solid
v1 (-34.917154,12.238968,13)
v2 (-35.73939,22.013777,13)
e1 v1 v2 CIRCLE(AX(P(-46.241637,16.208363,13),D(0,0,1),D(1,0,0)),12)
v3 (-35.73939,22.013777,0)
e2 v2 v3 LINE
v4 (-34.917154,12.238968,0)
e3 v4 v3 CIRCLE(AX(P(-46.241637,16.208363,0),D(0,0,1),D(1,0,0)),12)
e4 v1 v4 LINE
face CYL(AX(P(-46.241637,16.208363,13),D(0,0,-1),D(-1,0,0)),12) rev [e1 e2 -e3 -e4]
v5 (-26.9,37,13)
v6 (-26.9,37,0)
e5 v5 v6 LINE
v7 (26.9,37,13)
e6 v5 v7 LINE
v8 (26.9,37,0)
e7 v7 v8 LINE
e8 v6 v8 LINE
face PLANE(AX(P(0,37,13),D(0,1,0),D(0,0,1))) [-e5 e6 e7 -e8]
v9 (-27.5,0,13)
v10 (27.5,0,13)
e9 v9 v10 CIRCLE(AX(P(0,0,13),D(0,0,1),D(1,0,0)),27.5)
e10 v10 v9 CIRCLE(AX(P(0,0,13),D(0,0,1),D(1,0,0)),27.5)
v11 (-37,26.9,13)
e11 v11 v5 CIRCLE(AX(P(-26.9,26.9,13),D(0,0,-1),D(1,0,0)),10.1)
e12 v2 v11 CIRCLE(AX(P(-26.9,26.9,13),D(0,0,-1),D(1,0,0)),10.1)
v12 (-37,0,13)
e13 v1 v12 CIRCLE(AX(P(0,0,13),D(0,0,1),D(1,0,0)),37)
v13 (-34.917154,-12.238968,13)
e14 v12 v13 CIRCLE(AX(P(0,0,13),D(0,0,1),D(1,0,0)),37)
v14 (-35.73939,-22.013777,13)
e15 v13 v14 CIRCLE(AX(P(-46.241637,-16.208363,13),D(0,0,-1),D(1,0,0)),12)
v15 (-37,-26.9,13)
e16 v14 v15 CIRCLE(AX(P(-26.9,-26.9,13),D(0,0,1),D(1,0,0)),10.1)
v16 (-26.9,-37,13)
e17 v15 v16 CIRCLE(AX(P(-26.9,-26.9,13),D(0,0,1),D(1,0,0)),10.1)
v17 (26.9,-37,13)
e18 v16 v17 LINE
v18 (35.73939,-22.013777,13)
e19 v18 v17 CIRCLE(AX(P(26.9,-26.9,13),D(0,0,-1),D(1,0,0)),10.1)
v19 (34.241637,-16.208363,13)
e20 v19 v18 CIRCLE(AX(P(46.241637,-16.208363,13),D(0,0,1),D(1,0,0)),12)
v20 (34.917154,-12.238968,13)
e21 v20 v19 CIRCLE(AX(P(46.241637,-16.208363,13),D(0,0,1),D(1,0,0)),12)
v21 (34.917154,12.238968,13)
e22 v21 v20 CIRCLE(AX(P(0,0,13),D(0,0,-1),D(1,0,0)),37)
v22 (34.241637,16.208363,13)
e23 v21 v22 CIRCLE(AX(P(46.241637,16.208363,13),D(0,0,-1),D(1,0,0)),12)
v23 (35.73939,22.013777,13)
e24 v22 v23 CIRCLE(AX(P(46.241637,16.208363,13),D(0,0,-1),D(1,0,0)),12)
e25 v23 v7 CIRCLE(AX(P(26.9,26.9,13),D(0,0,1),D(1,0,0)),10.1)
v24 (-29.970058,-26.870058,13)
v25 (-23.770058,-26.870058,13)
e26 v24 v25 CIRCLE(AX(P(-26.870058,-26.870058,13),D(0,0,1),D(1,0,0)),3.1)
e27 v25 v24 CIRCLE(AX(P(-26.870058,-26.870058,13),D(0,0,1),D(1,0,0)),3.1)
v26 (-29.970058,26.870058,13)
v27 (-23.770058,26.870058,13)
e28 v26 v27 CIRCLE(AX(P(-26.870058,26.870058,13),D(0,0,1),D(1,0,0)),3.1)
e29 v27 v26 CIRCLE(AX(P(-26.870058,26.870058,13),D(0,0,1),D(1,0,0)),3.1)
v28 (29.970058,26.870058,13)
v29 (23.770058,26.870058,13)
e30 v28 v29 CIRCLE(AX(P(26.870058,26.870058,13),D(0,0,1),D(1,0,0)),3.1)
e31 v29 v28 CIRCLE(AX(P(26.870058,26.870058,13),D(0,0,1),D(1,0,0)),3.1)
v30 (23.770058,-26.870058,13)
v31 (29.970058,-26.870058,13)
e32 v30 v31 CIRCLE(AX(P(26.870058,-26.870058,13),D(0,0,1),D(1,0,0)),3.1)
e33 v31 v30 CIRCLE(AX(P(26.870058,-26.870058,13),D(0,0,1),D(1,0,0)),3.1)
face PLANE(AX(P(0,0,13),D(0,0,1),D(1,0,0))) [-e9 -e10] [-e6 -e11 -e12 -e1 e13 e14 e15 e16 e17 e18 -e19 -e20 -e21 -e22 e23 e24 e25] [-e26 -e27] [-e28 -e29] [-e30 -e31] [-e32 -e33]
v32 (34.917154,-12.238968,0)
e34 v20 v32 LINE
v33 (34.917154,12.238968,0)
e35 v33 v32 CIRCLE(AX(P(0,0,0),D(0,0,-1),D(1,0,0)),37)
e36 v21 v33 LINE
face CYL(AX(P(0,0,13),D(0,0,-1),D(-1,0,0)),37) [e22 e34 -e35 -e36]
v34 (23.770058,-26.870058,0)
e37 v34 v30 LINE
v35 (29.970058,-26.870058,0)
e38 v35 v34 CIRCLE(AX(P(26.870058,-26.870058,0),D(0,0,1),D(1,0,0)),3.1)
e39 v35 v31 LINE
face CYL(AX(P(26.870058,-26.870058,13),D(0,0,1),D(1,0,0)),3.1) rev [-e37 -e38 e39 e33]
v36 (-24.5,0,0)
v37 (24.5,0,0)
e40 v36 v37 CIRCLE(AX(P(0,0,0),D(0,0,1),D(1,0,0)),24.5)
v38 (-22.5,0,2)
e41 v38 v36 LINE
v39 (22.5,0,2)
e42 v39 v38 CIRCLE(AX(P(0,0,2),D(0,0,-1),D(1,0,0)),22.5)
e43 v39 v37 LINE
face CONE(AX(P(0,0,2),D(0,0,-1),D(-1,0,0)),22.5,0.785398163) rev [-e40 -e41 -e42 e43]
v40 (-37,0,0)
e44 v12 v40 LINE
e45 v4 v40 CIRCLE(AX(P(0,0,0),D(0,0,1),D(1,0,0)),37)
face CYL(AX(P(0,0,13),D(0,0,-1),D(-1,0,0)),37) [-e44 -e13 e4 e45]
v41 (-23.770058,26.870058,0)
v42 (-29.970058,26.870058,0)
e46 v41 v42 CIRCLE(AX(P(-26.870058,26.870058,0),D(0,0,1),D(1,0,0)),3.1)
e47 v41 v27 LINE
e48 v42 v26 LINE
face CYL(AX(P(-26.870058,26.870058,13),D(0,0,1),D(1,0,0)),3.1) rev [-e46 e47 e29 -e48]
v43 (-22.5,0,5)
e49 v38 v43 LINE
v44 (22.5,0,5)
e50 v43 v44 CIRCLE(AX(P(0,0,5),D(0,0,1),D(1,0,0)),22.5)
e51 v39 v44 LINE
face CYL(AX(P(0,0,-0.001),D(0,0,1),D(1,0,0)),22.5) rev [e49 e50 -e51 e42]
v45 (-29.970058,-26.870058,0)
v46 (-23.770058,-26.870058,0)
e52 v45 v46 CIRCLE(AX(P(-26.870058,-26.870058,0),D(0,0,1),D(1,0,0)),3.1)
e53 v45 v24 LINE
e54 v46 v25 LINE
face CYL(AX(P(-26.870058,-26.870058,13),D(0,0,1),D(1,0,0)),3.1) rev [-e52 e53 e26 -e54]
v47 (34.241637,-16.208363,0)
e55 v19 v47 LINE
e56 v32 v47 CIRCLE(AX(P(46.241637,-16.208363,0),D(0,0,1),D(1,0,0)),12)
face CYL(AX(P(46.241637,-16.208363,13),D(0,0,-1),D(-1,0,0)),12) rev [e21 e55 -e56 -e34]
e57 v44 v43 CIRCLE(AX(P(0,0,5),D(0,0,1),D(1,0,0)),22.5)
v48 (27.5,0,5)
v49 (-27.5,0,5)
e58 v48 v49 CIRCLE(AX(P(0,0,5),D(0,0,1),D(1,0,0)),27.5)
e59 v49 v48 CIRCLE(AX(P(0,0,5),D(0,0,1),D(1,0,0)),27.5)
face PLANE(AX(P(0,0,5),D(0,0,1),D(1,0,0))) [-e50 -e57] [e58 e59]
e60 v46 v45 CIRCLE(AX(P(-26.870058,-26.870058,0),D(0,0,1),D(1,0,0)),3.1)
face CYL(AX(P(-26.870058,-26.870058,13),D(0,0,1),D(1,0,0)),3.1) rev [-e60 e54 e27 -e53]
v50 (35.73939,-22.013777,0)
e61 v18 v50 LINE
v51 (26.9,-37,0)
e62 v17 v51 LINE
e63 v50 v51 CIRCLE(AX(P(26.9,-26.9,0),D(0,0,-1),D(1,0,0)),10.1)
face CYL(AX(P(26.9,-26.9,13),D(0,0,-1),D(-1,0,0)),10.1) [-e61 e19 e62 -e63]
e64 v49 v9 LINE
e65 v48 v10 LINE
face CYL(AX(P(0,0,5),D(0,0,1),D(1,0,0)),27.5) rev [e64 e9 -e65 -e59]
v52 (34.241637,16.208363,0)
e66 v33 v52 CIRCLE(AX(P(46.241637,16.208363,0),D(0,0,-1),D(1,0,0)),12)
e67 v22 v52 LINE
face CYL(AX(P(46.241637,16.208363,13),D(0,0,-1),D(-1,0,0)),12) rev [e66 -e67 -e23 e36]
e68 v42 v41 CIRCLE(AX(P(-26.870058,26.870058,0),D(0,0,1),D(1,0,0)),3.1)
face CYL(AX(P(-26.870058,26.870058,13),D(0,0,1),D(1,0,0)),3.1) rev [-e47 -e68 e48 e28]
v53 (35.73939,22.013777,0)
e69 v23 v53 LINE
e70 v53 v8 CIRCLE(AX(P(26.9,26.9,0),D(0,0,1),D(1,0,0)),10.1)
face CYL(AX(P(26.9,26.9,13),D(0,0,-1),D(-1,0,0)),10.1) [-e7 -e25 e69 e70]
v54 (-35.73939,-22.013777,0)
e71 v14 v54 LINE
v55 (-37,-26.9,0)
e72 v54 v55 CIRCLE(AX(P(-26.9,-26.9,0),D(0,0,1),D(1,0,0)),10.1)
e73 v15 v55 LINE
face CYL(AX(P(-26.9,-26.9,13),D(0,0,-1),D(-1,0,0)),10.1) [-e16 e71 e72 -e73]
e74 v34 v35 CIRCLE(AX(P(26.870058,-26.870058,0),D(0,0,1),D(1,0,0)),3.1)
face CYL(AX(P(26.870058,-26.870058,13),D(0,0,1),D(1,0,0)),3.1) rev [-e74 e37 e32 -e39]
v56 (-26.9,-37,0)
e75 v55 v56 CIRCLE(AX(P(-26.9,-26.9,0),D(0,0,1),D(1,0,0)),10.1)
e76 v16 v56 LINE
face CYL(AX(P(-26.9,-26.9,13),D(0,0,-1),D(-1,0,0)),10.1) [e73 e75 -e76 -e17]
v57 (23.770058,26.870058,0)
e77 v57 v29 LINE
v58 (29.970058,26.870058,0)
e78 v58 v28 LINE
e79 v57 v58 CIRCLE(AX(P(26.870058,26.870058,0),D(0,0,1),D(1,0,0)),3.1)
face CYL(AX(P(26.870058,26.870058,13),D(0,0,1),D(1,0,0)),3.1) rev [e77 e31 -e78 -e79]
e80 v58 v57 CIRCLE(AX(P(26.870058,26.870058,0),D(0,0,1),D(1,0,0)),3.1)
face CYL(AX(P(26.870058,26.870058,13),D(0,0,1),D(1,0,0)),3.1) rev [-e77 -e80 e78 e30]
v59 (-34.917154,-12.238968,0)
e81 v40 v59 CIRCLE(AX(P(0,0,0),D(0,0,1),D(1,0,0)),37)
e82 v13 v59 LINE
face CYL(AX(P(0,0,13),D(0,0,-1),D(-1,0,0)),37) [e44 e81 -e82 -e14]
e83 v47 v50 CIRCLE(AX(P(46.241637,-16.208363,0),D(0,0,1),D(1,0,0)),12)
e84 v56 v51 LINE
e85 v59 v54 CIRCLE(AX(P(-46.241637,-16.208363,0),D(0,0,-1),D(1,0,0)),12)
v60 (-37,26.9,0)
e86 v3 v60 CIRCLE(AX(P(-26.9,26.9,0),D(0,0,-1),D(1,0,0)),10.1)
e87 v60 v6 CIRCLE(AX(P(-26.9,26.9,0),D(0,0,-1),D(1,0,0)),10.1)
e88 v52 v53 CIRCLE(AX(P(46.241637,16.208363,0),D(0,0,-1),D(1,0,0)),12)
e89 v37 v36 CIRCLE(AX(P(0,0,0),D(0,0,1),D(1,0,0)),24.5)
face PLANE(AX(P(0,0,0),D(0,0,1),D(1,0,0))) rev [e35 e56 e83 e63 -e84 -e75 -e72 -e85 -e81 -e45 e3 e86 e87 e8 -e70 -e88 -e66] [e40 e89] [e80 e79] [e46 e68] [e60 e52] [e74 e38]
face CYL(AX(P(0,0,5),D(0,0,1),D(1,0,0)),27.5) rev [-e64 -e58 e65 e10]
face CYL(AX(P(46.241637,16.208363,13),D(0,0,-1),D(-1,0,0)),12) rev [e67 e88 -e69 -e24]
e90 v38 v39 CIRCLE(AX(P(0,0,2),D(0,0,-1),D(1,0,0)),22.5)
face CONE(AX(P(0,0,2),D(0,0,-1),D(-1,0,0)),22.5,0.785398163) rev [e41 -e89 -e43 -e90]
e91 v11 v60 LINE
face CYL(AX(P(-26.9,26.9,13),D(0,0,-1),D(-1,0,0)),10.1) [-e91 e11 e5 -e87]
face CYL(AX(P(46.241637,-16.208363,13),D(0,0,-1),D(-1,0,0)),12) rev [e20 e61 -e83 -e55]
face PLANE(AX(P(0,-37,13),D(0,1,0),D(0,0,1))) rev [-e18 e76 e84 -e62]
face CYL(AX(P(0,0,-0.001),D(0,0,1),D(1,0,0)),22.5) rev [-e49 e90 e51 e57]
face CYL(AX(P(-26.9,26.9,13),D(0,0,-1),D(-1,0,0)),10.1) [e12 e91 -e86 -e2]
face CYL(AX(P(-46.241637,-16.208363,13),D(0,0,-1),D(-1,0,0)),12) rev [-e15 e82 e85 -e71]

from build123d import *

# Parameters (mm, degrees)
EXTRUDE_1_DEPTH         = 13
HOLE_WIZARD_6_2_6_2_1_D = 6.2
SKETCH_4_R              = 27.5
CUT_EXTRUDE_1_DEPTH     = 8
CUT_EXTRUDE_2_REACH     = 54.934
SKETCH_5_R              = 22.5
CHAMFER_1_SIZE          = 2


with BuildPart() as part:
    # 草图1 → 凸台-拉伸1 (new body)
    with BuildSketch(Plane.XY):
        with BuildLine():
            Line((37, 0), (-37, 0))
            ThreePointArc((-37, 0), (-36.475571993, -6.2074671), (-34.917154173, -12.238968276))
            ThreePointArc((-34.917154173, -12.238968276), (-34.283867545, -17.214225736), (-35.739390486, -22.013776935))
            ThreePointArc((-35.739390486, -22.013776935), (-35.59944978, -32.031235087), (-26.9, -37))
            Line((-26.9, -37), (26.9, -37))
            ThreePointArc((26.9, -37), (35.59944978, -32.031235087), (35.739390486, -22.013776935))
            ThreePointArc((35.739390486, -22.013776935), (34.283867545, -17.214225736), (34.917154173, -12.238968276))
            ThreePointArc((34.917154173, -12.238968276), (36.475571993, -6.2074671), (37, 0))
        make_face()
        with BuildLine():
            Line((26.9, 37), (-26.9, 37))
            ThreePointArc((-26.9, 37), (-35.59944978, 32.031235087), (-35.739390486, 22.013776935))
            ThreePointArc((-35.739390486, 22.013776935), (-34.283867545, 17.214225736), (-34.917154173, 12.238968276))
            ThreePointArc((-34.917154173, 12.238968276), (-36.475571993, 6.2074671), (-37, 0))
            Line((-37, 0), (37, 0))
            ThreePointArc((37, 0), (36.475571993, 6.2074671), (34.917154173, 12.238968276))
            ThreePointArc((34.917154173, 12.238968276), (34.283867545, 17.214225736), (35.739390486, 22.013776935))
            ThreePointArc((35.739390486, 22.013776935), (35.59944978, 32.031235087), (26.9, 37))
        make_face()
    extrude(amount=EXTRUDE_1_DEPTH)

    # Ø6.2 (6.2) 直径孔1 (through all)
    with Locations(Plane(origin=(-26.870057685, 26.870057685, 13), x_dir=(1, 0, 0), z_dir=(0, 0, 1))):
        with Locations((0, 0), (53.74011537, 0), (53.74011537, -53.74011537), (0, -53.74011537)):
            Hole(HOLE_WIZARD_6_2_6_2_1_D / 2)

    # 草图4 → 切除-拉伸1 (cut)
    with BuildSketch(Plane.XY.offset(13)):
        Circle(SKETCH_4_R)
    extrude(amount=-CUT_EXTRUDE_1_DEPTH, mode=Mode.SUBTRACT)

    # 草图5 → 切除-拉伸2 (cut, up to next)
    with BuildSketch(Plane.XY.offset(5), mode=Mode.PRIVATE) as cut_extrude_2_sk1:
        Circle(SKETCH_5_R)
    cut_extrude_2_tool1 = extrude(cut_extrude_2_sk1.sketch, amount=-CUT_EXTRUDE_2_REACH, mode=Mode.PRIVATE) & part.part
    add(cut_extrude_2_tool1.solids().sort_by_distance((0, 0, 5))[0], mode=Mode.SUBTRACT)

    # 倒角1
    chamfer_1_edges = [part.edges().sort_by_distance(p)[0] for p in [
        (-22.5, 0, 0),
    ]]
    chamfer(chamfer_1_edges, length=CHAMFER_1_SIZE)


solid = part.part
